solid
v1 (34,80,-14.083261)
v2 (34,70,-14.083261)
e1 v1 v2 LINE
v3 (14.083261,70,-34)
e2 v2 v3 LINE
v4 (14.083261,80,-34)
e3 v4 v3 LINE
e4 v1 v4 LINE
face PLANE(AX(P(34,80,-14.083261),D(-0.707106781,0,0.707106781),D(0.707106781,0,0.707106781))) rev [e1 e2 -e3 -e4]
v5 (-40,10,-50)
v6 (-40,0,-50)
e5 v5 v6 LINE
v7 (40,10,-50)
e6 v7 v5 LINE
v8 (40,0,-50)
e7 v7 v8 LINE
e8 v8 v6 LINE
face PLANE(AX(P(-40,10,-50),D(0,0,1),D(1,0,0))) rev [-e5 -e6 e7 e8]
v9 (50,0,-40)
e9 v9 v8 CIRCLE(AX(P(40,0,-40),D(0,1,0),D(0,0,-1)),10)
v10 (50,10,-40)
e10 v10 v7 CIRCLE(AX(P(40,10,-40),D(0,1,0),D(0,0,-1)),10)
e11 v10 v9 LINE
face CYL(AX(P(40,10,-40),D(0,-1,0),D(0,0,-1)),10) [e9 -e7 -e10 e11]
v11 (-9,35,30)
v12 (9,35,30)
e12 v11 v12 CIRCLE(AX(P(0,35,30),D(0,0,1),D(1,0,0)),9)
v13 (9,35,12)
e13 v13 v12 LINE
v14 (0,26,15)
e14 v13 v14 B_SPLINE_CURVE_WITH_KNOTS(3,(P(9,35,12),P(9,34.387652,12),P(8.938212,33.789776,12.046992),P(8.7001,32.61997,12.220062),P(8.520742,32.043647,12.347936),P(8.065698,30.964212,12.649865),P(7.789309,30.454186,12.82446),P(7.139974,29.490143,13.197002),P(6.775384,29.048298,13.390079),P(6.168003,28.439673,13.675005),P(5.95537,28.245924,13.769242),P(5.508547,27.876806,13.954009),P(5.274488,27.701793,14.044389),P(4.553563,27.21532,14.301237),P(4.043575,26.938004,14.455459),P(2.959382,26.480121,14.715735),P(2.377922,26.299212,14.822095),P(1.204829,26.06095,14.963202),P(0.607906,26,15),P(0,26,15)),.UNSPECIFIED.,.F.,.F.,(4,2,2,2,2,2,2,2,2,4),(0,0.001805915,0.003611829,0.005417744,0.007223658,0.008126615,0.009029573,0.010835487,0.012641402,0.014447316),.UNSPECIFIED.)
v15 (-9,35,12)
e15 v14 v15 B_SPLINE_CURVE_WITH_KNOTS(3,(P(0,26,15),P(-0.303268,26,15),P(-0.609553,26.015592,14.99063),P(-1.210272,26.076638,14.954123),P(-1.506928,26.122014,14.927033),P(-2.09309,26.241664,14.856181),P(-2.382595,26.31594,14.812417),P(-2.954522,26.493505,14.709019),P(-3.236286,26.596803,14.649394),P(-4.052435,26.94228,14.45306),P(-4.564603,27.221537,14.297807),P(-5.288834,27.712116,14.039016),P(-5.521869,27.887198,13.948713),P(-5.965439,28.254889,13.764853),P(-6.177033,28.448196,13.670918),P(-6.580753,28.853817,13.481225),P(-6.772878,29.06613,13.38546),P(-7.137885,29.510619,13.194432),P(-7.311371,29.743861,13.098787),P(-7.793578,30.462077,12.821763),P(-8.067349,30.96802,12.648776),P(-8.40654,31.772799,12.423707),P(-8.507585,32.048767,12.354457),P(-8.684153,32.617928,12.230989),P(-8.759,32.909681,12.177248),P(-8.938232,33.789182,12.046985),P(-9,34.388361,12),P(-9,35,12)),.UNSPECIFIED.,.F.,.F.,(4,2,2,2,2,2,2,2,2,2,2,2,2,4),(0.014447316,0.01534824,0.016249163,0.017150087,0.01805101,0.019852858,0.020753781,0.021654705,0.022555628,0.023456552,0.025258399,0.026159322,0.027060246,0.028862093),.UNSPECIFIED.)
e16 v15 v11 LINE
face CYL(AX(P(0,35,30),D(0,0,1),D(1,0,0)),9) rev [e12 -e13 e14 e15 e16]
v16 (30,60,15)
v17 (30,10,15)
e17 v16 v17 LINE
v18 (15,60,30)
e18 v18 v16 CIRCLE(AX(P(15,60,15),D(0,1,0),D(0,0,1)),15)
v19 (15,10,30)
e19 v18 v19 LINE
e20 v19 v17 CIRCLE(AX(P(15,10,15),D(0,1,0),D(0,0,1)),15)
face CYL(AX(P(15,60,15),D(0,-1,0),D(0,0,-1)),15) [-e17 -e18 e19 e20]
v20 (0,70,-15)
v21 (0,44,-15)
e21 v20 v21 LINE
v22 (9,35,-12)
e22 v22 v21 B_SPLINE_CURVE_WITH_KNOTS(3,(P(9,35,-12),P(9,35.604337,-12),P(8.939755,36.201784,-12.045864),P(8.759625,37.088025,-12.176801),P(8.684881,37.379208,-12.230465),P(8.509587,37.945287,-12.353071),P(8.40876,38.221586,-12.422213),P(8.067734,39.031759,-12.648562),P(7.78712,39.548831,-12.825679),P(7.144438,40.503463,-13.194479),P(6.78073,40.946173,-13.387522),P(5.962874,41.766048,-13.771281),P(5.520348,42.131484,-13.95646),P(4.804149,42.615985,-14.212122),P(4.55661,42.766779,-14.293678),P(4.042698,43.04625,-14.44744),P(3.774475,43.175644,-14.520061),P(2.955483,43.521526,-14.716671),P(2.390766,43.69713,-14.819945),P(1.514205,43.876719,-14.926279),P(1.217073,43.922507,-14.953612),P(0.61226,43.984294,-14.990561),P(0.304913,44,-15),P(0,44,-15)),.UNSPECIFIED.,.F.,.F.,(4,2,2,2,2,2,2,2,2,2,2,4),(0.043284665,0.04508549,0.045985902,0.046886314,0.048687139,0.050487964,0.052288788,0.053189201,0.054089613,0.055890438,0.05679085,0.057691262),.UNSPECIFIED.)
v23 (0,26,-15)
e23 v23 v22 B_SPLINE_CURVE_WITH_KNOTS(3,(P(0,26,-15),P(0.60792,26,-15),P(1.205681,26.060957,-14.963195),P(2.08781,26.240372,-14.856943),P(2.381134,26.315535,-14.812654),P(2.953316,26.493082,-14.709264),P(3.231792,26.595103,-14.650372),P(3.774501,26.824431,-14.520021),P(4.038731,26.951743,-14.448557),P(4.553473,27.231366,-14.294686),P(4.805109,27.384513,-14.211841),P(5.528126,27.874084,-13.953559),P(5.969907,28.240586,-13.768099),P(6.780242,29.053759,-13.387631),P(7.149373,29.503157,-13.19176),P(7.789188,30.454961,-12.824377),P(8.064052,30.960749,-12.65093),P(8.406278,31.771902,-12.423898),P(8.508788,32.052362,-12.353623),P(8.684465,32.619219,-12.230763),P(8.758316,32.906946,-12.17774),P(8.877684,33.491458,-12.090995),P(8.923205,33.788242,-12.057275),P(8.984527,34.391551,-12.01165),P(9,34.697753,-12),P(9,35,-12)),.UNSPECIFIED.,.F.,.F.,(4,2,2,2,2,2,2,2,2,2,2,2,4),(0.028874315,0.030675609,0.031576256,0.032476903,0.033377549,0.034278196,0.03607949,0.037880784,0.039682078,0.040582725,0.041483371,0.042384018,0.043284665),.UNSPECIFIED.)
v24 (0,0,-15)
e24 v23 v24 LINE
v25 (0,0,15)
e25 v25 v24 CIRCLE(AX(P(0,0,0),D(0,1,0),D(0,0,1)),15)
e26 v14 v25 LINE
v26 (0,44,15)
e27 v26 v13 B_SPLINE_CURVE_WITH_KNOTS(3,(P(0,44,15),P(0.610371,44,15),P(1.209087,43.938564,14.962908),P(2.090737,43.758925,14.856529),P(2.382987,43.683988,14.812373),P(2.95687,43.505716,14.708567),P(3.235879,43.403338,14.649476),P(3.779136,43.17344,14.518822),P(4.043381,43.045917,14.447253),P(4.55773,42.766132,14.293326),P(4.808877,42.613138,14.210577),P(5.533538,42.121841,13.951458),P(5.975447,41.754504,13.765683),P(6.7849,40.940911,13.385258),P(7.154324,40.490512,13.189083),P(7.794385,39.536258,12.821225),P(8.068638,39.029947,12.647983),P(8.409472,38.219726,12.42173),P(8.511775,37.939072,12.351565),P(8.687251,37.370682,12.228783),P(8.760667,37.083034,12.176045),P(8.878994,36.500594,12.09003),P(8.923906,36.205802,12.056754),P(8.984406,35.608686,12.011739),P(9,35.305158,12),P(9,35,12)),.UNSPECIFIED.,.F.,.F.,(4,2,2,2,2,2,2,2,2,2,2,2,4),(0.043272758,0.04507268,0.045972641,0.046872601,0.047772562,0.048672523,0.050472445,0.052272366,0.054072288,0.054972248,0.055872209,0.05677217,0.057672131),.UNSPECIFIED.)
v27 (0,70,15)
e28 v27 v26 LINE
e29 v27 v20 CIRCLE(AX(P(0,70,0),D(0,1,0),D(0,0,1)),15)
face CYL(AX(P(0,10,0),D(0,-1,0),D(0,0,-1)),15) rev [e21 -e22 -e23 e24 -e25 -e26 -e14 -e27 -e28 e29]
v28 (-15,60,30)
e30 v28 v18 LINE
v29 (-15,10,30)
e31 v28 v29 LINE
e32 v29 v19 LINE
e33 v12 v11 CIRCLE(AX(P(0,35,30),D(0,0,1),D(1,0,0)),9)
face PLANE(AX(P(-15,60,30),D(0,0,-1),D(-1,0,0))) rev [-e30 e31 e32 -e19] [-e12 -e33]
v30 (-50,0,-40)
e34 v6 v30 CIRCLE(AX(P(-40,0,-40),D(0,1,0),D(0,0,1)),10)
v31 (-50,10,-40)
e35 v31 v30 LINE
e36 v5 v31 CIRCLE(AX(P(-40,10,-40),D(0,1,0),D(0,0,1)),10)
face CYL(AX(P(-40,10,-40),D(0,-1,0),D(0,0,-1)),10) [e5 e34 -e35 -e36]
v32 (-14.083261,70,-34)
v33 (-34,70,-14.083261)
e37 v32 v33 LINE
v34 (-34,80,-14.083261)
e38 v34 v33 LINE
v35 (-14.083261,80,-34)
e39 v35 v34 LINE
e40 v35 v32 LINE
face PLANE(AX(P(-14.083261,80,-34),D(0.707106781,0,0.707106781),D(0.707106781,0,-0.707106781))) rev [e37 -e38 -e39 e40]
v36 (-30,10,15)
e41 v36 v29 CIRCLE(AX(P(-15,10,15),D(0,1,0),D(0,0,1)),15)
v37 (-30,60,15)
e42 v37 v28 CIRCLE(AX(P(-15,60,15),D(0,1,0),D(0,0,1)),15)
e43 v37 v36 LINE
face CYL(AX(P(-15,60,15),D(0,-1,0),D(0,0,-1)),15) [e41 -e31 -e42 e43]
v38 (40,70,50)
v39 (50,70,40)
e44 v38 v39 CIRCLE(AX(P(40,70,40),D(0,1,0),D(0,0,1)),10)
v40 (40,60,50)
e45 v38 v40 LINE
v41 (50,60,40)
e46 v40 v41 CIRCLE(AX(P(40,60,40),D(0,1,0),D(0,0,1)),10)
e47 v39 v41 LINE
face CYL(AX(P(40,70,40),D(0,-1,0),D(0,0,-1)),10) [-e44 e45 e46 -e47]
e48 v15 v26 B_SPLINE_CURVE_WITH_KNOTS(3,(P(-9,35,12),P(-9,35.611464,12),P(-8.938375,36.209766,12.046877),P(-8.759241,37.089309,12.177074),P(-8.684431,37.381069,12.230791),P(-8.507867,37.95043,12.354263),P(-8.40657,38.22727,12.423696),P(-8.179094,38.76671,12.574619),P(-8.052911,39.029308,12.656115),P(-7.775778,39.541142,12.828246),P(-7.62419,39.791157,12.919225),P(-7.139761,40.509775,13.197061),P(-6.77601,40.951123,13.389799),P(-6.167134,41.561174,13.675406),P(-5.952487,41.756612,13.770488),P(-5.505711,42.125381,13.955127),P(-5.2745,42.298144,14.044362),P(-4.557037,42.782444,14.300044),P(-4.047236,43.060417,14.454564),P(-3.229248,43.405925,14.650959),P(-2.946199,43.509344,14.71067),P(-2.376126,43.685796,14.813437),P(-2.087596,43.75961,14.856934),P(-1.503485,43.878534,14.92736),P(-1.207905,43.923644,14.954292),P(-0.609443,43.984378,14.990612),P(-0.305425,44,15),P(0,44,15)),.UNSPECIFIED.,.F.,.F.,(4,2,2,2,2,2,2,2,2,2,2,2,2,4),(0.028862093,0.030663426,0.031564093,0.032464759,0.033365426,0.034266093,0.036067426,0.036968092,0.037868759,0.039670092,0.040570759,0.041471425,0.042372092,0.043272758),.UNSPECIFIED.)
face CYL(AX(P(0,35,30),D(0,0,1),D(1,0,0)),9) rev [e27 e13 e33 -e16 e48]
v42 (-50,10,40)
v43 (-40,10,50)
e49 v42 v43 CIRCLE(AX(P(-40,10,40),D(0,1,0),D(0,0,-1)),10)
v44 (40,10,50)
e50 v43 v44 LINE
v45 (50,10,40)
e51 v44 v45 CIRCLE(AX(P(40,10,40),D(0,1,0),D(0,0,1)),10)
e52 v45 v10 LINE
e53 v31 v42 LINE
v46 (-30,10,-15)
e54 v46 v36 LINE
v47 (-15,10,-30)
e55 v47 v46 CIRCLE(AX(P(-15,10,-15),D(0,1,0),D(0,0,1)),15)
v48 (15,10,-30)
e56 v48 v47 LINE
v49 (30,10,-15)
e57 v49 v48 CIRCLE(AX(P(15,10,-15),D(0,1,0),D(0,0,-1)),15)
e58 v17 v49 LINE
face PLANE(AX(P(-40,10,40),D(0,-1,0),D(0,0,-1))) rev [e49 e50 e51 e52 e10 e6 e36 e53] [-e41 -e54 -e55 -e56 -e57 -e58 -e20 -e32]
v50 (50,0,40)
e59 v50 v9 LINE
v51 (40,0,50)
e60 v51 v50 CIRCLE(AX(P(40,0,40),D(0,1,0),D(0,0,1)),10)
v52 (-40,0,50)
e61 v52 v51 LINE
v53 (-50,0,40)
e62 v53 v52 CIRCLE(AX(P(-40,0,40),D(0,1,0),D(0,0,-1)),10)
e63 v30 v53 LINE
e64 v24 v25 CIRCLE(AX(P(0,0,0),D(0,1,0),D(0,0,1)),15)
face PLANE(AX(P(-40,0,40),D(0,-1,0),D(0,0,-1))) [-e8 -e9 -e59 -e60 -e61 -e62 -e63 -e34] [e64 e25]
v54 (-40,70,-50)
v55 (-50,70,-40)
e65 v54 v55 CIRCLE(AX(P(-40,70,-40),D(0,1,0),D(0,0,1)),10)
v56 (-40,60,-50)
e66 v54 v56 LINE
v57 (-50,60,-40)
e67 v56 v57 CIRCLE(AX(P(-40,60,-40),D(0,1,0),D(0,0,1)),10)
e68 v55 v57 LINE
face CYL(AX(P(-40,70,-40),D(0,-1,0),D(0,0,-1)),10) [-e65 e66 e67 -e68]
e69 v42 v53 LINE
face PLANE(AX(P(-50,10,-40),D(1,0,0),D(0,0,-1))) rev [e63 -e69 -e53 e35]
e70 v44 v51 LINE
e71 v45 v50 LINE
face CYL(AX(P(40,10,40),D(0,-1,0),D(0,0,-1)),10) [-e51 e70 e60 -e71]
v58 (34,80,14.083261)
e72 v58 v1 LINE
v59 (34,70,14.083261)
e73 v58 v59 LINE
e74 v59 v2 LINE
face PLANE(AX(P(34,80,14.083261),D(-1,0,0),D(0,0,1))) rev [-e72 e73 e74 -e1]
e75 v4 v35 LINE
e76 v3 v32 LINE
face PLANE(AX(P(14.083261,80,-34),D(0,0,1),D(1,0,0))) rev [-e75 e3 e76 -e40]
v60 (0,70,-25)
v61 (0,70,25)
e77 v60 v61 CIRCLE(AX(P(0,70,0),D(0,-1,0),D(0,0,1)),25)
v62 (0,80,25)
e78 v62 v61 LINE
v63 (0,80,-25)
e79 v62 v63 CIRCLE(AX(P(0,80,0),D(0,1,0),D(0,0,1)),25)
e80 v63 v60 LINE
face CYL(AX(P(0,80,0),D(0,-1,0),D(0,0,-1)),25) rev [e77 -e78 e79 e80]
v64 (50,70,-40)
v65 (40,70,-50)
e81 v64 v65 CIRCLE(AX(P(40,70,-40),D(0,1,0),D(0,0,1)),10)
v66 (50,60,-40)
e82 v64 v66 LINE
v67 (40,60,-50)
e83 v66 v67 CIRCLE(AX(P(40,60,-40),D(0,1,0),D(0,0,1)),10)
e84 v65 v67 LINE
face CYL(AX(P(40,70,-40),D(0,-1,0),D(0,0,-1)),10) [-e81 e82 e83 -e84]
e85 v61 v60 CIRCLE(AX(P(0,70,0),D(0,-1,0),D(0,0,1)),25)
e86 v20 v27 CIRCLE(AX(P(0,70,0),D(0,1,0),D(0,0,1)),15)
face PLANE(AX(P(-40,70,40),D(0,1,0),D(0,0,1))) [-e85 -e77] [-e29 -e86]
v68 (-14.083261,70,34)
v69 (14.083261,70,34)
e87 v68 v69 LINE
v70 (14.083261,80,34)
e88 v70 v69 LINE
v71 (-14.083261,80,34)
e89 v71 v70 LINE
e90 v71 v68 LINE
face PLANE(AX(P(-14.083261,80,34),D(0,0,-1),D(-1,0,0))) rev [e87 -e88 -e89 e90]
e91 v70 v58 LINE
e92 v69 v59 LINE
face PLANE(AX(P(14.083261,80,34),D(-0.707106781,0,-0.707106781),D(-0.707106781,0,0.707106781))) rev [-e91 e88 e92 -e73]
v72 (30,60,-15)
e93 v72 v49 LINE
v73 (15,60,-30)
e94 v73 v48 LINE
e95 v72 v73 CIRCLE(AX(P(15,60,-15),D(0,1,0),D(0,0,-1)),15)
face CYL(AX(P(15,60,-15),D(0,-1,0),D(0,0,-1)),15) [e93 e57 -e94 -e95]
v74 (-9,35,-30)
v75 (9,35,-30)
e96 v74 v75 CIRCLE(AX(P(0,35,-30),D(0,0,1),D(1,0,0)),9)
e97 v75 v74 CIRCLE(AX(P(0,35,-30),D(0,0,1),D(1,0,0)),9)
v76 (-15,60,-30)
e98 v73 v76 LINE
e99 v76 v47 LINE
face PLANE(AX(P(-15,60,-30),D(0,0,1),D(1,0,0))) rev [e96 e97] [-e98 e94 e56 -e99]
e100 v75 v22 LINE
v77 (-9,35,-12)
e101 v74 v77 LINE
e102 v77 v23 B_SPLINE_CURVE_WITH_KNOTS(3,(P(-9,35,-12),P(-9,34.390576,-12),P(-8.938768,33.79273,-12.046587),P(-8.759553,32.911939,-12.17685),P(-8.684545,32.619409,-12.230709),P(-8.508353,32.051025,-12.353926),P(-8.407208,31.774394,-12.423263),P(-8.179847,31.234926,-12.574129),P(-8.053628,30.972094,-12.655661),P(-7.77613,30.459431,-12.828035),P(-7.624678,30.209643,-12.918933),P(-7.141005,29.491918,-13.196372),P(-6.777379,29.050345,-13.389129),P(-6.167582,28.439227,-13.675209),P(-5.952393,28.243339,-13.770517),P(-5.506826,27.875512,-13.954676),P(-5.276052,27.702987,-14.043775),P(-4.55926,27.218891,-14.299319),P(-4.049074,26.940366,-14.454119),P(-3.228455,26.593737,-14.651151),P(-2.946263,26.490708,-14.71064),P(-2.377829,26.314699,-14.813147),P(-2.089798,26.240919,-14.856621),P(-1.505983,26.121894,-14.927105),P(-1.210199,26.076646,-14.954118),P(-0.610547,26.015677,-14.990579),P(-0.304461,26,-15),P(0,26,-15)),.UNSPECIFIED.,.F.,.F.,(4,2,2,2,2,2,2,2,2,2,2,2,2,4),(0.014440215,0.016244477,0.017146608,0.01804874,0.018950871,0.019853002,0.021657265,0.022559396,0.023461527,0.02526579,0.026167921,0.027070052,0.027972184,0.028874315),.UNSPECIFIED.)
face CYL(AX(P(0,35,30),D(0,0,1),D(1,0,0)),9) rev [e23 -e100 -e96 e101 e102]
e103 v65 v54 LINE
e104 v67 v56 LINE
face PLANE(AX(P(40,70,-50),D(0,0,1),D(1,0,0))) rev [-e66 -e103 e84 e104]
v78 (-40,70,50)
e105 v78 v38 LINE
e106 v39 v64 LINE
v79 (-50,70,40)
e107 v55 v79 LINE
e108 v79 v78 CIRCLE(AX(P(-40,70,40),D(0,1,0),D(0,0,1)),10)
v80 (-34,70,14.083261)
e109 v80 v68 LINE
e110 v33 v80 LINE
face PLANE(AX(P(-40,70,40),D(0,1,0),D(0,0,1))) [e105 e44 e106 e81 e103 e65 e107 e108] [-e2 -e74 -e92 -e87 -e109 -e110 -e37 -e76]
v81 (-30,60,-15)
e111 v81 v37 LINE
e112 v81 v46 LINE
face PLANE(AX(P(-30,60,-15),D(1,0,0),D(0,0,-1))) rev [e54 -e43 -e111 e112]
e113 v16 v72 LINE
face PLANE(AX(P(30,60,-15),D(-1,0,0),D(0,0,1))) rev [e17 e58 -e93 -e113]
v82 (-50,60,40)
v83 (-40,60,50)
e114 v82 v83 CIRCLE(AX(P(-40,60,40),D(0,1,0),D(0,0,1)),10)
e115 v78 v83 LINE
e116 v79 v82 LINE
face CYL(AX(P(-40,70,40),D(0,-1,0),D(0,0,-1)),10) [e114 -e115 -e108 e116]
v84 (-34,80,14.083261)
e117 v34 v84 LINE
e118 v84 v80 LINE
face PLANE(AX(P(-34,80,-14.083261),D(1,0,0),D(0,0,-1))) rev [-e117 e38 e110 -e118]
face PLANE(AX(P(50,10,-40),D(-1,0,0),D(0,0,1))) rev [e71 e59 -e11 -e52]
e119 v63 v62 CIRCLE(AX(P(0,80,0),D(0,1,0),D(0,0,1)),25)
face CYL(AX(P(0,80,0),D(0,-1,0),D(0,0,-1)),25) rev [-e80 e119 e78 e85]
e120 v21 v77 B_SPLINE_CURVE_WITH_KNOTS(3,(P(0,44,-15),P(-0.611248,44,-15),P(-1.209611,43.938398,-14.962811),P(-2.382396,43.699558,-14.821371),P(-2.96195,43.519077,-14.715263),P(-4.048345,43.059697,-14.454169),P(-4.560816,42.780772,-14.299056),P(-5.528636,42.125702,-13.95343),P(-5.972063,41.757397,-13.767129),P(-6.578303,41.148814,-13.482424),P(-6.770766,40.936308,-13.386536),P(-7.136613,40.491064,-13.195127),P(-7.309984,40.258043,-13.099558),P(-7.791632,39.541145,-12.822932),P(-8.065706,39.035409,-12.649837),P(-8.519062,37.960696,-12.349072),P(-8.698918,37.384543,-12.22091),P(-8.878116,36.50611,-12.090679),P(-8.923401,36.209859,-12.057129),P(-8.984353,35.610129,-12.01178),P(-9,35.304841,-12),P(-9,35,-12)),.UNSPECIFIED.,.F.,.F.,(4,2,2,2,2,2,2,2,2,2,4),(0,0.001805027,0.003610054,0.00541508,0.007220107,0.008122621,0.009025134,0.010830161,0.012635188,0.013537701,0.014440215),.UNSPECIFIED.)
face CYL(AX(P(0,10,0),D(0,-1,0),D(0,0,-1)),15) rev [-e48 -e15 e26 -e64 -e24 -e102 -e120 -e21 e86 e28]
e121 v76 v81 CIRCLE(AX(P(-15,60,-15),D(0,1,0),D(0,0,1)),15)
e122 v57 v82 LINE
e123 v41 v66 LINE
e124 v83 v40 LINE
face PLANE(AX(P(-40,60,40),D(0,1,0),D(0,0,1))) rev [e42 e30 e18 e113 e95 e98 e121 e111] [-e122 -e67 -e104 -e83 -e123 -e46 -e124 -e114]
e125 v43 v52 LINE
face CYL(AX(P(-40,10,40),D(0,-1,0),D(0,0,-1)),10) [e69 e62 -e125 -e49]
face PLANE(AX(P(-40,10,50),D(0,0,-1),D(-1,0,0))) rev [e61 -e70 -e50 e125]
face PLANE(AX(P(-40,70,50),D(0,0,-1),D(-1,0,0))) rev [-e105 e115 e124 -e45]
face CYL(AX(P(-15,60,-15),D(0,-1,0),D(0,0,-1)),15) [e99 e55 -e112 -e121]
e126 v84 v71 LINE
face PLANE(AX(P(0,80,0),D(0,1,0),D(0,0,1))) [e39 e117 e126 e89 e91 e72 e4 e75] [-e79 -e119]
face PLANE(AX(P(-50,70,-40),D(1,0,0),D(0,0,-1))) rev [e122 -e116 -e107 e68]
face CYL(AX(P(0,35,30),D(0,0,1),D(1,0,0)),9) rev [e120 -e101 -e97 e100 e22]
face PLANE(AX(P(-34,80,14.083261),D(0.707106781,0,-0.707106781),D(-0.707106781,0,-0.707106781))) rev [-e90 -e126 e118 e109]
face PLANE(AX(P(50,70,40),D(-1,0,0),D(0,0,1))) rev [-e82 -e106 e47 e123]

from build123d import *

# Parameters (mm, degrees)
BASE_PLATE_SKETCH_R    = 15
BASE_PLATE_DEPTH       = 10
CENTRE_COLUMN_SKETCH_R = 15
CENTRE_COLUMN_DEPTH    = 50
TOP_PLATE_SKETCH_R     = 15
TOP_PLATE_DEPTH        = 10
OCTAGON_BOSS_SKETCH_R  = 25
OCTAGON_BOSS_DEPTH     = 10
CROSS_HOLE_18_D        = 18


with BuildPart() as part:
    # Base Plate Sketch → Base Plate (new body)
    with BuildSketch(Plane(origin=(0, 0, 0), x_dir=(1, 0, 0), z_dir=(0, 1, 0))):
        with BuildLine():
            Line((-40, 50), (40, 50))
            ThreePointArc((40, 50), (47.071067812, 47.071067812), (50, 40))
            Line((50, 40), (50, -40))
            ThreePointArc((50, -40), (47.071067812, -47.071067812), (40, -50))
            Line((40, -50), (-40, -50))
            ThreePointArc((-40, -50), (-47.071067812, -47.071067812), (-50, -40))
            Line((-50, -40), (-50, 40))
            ThreePointArc((-50, 40), (-47.071067812, 47.071067812), (-40, 50))
        make_face()
        with Locations(Location((0, 0, 0), (0, 0, 270))):
            Circle(BASE_PLATE_SKETCH_R, mode=Mode.SUBTRACT)
    extrude(amount=BASE_PLATE_DEPTH)

    # Centre Column Sketch → Centre Column (add)
    with BuildSketch(Plane(origin=(0, 10, 0), x_dir=(1, 0, 0), z_dir=(0, 1, 0))):
        with BuildLine():
            Line((-15, 30), (15, 30))
            ThreePointArc((15, 30), (25.606601718, 25.606601718), (30, 15))
            Line((30, 15), (30, -15))
            ThreePointArc((30, -15), (25.606601718, -25.606601718), (15, -30))
            Line((15, -30), (-15, -30))
            ThreePointArc((-15, -30), (-25.606601718, -25.606601718), (-30, -15))
            Line((-30, -15), (-30, 15))
            ThreePointArc((-30, 15), (-25.606601718, 25.606601718), (-15, 30))
        make_face()
        with Locations(Location((0, 0, 0), (0, 0, 270))):
            Circle(CENTRE_COLUMN_SKETCH_R, mode=Mode.SUBTRACT)
    extrude(amount=CENTRE_COLUMN_DEPTH)

    # Top Plate Sketch → Top Plate (add)
    with BuildSketch(Plane(origin=(0, 60, 0), x_dir=(1, 0, 0), z_dir=(0, 1, 0))):
        with BuildLine():
            Line((-40, -50), (40, -50))
            ThreePointArc((40, -50), (47.071067812, -47.071067812), (50, -40))
            Line((50, -40), (50, 40))
            ThreePointArc((50, 40), (47.071067812, 47.071067812), (40, 50))
            Line((40, 50), (-40, 50))
            ThreePointArc((-40, 50), (-47.071067812, 47.071067812), (-50, 40))
            Line((-50, 40), (-50, -40))
            ThreePointArc((-50, -40), (-47.071067812, -47.071067812), (-40, -50))
        make_face()
        with Locations(Location((0, 0, 0), (0, 0, 270))):
            Circle(TOP_PLATE_SKETCH_R, mode=Mode.SUBTRACT)
    extrude(amount=TOP_PLATE_DEPTH)

    # Octagon Boss Sketch → Octagon Boss (add)
    with BuildSketch(Plane(origin=(0, 70, 0), x_dir=(1, 0, 0), z_dir=(0, 1, 0))):
        Polygon((34, -14.083261121), (34, 14.083261121), (14.083261121, 34), (-14.083261121, 34), (-34, 14.083261121), (-34, -14.083261121), (-14.083261121, -34), (14.083261121, -34), align=None)
        with Locations(Location((0, 0, 0), (0, 0, 270))):
            Circle(OCTAGON_BOSS_SKETCH_R, mode=Mode.SUBTRACT)
    extrude(amount=OCTAGON_BOSS_DEPTH)

    # Cross Hole Ø18 (through all)
    with Locations(Plane.XY.offset(30)):
        with Locations((0, 35)):
            Hole(CROSS_HOLE_18_D / 2)


solid = part.part
